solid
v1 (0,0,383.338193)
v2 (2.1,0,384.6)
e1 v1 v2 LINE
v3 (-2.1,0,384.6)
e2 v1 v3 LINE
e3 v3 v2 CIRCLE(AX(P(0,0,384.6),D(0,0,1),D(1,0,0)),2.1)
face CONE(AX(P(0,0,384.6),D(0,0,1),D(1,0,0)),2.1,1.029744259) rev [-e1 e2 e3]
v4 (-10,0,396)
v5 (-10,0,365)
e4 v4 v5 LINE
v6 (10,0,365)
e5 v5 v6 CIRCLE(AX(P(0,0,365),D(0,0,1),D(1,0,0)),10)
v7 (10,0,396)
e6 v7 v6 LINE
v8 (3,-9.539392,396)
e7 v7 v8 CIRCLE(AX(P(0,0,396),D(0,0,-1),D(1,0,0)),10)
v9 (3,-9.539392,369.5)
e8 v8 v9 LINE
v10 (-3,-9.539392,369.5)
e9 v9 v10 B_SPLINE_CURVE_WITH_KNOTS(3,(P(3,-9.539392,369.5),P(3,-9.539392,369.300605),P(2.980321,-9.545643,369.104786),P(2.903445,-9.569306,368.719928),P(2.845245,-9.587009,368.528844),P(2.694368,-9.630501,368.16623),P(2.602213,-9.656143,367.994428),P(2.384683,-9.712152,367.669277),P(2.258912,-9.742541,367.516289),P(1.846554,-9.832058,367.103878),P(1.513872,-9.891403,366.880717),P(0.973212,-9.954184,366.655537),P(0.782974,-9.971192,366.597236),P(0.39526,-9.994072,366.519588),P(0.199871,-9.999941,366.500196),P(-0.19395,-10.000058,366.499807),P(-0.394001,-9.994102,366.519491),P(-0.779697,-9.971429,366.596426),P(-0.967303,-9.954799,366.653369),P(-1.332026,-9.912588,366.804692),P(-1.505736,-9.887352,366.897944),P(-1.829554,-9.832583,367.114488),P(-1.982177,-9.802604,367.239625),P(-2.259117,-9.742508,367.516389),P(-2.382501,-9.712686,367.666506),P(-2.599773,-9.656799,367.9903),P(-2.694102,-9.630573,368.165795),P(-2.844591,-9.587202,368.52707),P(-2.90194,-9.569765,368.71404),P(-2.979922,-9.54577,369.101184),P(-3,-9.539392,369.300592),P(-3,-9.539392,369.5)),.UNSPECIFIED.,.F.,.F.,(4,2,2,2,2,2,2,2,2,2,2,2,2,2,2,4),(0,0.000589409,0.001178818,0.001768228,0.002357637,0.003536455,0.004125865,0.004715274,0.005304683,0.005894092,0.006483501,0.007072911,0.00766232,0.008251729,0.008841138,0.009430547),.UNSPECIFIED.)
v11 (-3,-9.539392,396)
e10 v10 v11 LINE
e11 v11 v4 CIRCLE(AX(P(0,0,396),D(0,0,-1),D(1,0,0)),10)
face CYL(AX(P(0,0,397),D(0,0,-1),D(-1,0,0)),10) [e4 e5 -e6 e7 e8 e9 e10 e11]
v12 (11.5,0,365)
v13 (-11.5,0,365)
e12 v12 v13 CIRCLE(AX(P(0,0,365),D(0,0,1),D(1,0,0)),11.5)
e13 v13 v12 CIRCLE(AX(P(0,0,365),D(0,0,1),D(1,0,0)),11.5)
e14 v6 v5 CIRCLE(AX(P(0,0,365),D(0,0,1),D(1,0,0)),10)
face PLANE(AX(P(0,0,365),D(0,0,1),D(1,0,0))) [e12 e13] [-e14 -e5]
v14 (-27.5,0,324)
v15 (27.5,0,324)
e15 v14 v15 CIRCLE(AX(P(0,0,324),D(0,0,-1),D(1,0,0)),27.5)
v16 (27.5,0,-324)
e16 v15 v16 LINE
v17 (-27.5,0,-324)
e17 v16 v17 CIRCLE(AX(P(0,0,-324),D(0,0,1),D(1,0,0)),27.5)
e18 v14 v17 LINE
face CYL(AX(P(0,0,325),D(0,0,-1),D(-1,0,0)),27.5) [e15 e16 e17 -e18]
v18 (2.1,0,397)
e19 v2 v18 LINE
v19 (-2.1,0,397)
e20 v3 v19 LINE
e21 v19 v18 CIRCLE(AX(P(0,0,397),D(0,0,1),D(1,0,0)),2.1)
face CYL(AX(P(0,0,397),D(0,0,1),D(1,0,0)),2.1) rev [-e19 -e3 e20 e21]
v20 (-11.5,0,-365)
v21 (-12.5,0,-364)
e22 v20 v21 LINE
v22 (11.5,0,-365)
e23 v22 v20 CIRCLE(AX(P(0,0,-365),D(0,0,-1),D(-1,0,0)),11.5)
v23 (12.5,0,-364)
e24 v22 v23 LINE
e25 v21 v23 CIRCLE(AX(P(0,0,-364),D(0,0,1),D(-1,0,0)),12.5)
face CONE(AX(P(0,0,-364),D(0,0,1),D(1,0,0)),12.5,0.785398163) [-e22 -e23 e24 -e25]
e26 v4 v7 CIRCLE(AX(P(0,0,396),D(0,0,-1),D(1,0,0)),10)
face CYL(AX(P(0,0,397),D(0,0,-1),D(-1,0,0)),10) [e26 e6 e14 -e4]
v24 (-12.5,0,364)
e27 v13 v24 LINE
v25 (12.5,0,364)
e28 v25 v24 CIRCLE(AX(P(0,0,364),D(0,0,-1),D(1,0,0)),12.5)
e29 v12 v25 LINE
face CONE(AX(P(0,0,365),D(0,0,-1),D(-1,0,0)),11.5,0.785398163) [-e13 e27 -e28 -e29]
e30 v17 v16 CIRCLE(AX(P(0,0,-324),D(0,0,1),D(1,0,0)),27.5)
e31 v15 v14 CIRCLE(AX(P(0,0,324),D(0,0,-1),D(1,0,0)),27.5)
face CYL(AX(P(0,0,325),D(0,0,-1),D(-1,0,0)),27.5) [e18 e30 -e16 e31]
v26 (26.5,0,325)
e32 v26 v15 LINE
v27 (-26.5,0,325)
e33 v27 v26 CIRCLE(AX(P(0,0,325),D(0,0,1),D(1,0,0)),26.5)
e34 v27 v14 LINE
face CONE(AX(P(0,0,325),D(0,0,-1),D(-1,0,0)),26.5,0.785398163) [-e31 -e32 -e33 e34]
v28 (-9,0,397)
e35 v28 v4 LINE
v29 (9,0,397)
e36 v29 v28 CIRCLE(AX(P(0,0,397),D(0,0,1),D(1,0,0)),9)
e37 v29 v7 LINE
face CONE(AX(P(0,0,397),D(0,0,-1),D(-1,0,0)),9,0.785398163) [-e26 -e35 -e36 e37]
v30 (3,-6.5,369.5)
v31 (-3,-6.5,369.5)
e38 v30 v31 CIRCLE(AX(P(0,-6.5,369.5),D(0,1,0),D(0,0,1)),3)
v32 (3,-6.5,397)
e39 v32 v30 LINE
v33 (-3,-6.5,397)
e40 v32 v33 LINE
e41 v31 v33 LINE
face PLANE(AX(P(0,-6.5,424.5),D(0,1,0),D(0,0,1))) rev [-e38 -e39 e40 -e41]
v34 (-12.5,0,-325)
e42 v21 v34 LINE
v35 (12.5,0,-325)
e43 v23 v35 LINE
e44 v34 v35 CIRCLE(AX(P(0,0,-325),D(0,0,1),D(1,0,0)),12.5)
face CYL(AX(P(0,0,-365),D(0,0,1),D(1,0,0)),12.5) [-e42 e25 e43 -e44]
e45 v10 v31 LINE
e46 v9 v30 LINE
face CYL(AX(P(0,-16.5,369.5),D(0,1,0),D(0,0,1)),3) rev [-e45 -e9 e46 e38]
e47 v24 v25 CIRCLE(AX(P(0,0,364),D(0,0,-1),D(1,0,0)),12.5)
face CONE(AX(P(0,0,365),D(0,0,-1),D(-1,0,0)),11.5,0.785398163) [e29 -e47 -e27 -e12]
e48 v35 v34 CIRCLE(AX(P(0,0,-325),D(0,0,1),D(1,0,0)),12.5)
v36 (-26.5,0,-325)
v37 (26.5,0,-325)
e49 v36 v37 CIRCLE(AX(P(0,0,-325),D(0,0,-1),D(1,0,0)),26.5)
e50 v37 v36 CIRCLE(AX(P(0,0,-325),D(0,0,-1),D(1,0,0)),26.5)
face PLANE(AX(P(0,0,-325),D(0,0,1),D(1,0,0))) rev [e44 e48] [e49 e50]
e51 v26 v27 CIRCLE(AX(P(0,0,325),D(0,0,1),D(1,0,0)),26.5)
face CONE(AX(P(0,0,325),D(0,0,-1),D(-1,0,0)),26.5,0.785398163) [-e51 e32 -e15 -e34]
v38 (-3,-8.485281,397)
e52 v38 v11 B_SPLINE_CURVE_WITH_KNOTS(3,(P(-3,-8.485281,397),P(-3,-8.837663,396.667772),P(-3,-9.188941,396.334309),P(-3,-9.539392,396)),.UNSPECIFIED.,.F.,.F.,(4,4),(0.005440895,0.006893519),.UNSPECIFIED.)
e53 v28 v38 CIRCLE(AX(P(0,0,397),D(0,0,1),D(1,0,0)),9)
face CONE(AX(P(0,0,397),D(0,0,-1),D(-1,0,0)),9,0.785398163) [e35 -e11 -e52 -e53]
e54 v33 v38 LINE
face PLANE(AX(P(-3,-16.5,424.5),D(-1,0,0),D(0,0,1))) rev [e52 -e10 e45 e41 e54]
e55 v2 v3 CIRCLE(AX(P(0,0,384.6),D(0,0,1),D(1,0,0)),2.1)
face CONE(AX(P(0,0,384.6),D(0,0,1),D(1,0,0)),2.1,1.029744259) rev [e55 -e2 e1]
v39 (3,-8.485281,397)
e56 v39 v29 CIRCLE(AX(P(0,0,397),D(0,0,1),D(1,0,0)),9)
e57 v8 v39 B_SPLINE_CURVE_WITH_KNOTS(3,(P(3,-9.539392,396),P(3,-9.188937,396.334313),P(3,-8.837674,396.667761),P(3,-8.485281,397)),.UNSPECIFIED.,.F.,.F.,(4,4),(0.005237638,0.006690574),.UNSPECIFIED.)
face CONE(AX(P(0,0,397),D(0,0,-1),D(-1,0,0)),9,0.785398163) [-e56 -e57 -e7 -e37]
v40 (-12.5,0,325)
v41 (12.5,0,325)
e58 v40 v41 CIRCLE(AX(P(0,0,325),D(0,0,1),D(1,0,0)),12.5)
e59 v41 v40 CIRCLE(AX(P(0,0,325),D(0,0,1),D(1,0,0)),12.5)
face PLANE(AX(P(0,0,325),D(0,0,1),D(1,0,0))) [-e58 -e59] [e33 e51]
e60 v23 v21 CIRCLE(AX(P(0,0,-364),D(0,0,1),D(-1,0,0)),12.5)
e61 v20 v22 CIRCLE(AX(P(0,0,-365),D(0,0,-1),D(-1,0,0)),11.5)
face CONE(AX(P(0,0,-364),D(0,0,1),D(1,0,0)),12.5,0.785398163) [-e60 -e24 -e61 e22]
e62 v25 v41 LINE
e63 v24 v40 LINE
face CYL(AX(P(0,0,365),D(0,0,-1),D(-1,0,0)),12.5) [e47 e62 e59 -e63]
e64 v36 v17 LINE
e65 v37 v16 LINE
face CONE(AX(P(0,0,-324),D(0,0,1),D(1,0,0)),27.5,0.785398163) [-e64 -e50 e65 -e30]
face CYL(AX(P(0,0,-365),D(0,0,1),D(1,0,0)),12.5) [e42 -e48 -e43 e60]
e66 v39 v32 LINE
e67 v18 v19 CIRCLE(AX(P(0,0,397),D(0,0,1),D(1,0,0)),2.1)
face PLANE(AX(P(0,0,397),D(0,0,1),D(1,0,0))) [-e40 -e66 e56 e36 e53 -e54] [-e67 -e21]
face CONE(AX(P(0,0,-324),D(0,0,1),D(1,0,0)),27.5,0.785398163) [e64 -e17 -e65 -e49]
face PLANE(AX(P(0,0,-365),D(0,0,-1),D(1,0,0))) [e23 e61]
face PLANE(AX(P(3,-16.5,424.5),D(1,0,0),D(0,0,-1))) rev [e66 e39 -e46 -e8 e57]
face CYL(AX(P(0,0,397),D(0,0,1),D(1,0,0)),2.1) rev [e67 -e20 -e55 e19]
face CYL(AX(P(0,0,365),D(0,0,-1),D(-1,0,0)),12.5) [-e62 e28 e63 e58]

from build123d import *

# Parameters (mm, degrees)
SKETCH1_R             = 27.5
BOSS_EXTRUDE1_DEPTH   = 325
SKETCH2_R             = 12.5
BOSS_EXTRUDE2_DEPTH   = 40
CHAMFER1_SIZE         = 1
SKETCH3_R             = 10
BOSS_EXTRUDE3_DEPTH   = 32
CHAMFER2_SIZE         = 1
CUT_EXTRUDE1_START    = -6.5
CUT_EXTRUDE1_DEPTH    = 10
M5_TAPPED_HOLE1_D     = 4.2
M5_TAPPED_HOLE1_DEPTH = 12.4
M5_TAPPED_HOLE1_TIP   = 1.2618073


with BuildPart() as part:
    # Sketch1 → Boss-Extrude1 (new, symmetric)
    with BuildSketch(Plane.XY):
        Circle(SKETCH1_R)
    extrude(amount=BOSS_EXTRUDE1_DEPTH, both=True)

    # Sketch2 → Boss-Extrude2 (add)
    with BuildSketch(Plane.XY.offset(325)):
        Circle(SKETCH2_R)
    boss_extrude2 = extrude(amount=BOSS_EXTRUDE2_DEPTH)

    # Mirror1: Boss-Extrude2 across plane
    add(boss_extrude2.mirror(Plane.XY))

    # Chamfer1
    chamfer1_edges = [part.edges().sort_by_distance(p)[0] for p in [
        (-12.5, 0, -365),
        (-27.5, 0, -325),
        (-27.5, 0, 325),
        (-12.5, 0, 365),
    ]]
    chamfer(chamfer1_edges, length=CHAMFER1_SIZE)

    # Sketch3 → Boss-Extrude3 (add)
    with BuildSketch(Plane.XY.offset(365)):
        Circle(SKETCH3_R)
    extrude(amount=BOSS_EXTRUDE3_DEPTH)

    # Chamfer2
    chamfer2_edges = [part.edges().sort_by_distance(p)[0] for p in [
        (-10, 0, 397),
    ]]
    chamfer(chamfer2_edges, length=CHAMFER2_SIZE)

    # Sketch4 → Cut-Extrude1 (cut)
    with BuildSketch(Plane(origin=(0, 0, 0), x_dir=(1, 0, 0), z_dir=(0, 1, 0)).offset(CUT_EXTRUDE1_START)):
        with BuildLine():
            Line((-3, -424.5), (-3, -369.5))
            ThreePointArc((-3, -369.5), (0, -366.5), (3, -369.5))
            Line((3, -369.5), (3, -424.5))
            ThreePointArc((3, -424.5), (0, -427.5), (-3, -424.5))
        make_face()
    extrude(amount=-CUT_EXTRUDE1_DEPTH, mode=Mode.SUBTRACT)

    # M5 Tapped Hole1
    with Locations(Plane.XY.offset(397)):
        with Locations((0, 0)):
            Hole(M5_TAPPED_HOLE1_D / 2, depth=M5_TAPPED_HOLE1_DEPTH)
            with Locations((0, 0, -(M5_TAPPED_HOLE1_DEPTH + M5_TAPPED_HOLE1_TIP / 2))):  # 118° drill point
                Cone(0, M5_TAPPED_HOLE1_D / 2, M5_TAPPED_HOLE1_TIP, mode=Mode.SUBTRACT)


solid = part.part
